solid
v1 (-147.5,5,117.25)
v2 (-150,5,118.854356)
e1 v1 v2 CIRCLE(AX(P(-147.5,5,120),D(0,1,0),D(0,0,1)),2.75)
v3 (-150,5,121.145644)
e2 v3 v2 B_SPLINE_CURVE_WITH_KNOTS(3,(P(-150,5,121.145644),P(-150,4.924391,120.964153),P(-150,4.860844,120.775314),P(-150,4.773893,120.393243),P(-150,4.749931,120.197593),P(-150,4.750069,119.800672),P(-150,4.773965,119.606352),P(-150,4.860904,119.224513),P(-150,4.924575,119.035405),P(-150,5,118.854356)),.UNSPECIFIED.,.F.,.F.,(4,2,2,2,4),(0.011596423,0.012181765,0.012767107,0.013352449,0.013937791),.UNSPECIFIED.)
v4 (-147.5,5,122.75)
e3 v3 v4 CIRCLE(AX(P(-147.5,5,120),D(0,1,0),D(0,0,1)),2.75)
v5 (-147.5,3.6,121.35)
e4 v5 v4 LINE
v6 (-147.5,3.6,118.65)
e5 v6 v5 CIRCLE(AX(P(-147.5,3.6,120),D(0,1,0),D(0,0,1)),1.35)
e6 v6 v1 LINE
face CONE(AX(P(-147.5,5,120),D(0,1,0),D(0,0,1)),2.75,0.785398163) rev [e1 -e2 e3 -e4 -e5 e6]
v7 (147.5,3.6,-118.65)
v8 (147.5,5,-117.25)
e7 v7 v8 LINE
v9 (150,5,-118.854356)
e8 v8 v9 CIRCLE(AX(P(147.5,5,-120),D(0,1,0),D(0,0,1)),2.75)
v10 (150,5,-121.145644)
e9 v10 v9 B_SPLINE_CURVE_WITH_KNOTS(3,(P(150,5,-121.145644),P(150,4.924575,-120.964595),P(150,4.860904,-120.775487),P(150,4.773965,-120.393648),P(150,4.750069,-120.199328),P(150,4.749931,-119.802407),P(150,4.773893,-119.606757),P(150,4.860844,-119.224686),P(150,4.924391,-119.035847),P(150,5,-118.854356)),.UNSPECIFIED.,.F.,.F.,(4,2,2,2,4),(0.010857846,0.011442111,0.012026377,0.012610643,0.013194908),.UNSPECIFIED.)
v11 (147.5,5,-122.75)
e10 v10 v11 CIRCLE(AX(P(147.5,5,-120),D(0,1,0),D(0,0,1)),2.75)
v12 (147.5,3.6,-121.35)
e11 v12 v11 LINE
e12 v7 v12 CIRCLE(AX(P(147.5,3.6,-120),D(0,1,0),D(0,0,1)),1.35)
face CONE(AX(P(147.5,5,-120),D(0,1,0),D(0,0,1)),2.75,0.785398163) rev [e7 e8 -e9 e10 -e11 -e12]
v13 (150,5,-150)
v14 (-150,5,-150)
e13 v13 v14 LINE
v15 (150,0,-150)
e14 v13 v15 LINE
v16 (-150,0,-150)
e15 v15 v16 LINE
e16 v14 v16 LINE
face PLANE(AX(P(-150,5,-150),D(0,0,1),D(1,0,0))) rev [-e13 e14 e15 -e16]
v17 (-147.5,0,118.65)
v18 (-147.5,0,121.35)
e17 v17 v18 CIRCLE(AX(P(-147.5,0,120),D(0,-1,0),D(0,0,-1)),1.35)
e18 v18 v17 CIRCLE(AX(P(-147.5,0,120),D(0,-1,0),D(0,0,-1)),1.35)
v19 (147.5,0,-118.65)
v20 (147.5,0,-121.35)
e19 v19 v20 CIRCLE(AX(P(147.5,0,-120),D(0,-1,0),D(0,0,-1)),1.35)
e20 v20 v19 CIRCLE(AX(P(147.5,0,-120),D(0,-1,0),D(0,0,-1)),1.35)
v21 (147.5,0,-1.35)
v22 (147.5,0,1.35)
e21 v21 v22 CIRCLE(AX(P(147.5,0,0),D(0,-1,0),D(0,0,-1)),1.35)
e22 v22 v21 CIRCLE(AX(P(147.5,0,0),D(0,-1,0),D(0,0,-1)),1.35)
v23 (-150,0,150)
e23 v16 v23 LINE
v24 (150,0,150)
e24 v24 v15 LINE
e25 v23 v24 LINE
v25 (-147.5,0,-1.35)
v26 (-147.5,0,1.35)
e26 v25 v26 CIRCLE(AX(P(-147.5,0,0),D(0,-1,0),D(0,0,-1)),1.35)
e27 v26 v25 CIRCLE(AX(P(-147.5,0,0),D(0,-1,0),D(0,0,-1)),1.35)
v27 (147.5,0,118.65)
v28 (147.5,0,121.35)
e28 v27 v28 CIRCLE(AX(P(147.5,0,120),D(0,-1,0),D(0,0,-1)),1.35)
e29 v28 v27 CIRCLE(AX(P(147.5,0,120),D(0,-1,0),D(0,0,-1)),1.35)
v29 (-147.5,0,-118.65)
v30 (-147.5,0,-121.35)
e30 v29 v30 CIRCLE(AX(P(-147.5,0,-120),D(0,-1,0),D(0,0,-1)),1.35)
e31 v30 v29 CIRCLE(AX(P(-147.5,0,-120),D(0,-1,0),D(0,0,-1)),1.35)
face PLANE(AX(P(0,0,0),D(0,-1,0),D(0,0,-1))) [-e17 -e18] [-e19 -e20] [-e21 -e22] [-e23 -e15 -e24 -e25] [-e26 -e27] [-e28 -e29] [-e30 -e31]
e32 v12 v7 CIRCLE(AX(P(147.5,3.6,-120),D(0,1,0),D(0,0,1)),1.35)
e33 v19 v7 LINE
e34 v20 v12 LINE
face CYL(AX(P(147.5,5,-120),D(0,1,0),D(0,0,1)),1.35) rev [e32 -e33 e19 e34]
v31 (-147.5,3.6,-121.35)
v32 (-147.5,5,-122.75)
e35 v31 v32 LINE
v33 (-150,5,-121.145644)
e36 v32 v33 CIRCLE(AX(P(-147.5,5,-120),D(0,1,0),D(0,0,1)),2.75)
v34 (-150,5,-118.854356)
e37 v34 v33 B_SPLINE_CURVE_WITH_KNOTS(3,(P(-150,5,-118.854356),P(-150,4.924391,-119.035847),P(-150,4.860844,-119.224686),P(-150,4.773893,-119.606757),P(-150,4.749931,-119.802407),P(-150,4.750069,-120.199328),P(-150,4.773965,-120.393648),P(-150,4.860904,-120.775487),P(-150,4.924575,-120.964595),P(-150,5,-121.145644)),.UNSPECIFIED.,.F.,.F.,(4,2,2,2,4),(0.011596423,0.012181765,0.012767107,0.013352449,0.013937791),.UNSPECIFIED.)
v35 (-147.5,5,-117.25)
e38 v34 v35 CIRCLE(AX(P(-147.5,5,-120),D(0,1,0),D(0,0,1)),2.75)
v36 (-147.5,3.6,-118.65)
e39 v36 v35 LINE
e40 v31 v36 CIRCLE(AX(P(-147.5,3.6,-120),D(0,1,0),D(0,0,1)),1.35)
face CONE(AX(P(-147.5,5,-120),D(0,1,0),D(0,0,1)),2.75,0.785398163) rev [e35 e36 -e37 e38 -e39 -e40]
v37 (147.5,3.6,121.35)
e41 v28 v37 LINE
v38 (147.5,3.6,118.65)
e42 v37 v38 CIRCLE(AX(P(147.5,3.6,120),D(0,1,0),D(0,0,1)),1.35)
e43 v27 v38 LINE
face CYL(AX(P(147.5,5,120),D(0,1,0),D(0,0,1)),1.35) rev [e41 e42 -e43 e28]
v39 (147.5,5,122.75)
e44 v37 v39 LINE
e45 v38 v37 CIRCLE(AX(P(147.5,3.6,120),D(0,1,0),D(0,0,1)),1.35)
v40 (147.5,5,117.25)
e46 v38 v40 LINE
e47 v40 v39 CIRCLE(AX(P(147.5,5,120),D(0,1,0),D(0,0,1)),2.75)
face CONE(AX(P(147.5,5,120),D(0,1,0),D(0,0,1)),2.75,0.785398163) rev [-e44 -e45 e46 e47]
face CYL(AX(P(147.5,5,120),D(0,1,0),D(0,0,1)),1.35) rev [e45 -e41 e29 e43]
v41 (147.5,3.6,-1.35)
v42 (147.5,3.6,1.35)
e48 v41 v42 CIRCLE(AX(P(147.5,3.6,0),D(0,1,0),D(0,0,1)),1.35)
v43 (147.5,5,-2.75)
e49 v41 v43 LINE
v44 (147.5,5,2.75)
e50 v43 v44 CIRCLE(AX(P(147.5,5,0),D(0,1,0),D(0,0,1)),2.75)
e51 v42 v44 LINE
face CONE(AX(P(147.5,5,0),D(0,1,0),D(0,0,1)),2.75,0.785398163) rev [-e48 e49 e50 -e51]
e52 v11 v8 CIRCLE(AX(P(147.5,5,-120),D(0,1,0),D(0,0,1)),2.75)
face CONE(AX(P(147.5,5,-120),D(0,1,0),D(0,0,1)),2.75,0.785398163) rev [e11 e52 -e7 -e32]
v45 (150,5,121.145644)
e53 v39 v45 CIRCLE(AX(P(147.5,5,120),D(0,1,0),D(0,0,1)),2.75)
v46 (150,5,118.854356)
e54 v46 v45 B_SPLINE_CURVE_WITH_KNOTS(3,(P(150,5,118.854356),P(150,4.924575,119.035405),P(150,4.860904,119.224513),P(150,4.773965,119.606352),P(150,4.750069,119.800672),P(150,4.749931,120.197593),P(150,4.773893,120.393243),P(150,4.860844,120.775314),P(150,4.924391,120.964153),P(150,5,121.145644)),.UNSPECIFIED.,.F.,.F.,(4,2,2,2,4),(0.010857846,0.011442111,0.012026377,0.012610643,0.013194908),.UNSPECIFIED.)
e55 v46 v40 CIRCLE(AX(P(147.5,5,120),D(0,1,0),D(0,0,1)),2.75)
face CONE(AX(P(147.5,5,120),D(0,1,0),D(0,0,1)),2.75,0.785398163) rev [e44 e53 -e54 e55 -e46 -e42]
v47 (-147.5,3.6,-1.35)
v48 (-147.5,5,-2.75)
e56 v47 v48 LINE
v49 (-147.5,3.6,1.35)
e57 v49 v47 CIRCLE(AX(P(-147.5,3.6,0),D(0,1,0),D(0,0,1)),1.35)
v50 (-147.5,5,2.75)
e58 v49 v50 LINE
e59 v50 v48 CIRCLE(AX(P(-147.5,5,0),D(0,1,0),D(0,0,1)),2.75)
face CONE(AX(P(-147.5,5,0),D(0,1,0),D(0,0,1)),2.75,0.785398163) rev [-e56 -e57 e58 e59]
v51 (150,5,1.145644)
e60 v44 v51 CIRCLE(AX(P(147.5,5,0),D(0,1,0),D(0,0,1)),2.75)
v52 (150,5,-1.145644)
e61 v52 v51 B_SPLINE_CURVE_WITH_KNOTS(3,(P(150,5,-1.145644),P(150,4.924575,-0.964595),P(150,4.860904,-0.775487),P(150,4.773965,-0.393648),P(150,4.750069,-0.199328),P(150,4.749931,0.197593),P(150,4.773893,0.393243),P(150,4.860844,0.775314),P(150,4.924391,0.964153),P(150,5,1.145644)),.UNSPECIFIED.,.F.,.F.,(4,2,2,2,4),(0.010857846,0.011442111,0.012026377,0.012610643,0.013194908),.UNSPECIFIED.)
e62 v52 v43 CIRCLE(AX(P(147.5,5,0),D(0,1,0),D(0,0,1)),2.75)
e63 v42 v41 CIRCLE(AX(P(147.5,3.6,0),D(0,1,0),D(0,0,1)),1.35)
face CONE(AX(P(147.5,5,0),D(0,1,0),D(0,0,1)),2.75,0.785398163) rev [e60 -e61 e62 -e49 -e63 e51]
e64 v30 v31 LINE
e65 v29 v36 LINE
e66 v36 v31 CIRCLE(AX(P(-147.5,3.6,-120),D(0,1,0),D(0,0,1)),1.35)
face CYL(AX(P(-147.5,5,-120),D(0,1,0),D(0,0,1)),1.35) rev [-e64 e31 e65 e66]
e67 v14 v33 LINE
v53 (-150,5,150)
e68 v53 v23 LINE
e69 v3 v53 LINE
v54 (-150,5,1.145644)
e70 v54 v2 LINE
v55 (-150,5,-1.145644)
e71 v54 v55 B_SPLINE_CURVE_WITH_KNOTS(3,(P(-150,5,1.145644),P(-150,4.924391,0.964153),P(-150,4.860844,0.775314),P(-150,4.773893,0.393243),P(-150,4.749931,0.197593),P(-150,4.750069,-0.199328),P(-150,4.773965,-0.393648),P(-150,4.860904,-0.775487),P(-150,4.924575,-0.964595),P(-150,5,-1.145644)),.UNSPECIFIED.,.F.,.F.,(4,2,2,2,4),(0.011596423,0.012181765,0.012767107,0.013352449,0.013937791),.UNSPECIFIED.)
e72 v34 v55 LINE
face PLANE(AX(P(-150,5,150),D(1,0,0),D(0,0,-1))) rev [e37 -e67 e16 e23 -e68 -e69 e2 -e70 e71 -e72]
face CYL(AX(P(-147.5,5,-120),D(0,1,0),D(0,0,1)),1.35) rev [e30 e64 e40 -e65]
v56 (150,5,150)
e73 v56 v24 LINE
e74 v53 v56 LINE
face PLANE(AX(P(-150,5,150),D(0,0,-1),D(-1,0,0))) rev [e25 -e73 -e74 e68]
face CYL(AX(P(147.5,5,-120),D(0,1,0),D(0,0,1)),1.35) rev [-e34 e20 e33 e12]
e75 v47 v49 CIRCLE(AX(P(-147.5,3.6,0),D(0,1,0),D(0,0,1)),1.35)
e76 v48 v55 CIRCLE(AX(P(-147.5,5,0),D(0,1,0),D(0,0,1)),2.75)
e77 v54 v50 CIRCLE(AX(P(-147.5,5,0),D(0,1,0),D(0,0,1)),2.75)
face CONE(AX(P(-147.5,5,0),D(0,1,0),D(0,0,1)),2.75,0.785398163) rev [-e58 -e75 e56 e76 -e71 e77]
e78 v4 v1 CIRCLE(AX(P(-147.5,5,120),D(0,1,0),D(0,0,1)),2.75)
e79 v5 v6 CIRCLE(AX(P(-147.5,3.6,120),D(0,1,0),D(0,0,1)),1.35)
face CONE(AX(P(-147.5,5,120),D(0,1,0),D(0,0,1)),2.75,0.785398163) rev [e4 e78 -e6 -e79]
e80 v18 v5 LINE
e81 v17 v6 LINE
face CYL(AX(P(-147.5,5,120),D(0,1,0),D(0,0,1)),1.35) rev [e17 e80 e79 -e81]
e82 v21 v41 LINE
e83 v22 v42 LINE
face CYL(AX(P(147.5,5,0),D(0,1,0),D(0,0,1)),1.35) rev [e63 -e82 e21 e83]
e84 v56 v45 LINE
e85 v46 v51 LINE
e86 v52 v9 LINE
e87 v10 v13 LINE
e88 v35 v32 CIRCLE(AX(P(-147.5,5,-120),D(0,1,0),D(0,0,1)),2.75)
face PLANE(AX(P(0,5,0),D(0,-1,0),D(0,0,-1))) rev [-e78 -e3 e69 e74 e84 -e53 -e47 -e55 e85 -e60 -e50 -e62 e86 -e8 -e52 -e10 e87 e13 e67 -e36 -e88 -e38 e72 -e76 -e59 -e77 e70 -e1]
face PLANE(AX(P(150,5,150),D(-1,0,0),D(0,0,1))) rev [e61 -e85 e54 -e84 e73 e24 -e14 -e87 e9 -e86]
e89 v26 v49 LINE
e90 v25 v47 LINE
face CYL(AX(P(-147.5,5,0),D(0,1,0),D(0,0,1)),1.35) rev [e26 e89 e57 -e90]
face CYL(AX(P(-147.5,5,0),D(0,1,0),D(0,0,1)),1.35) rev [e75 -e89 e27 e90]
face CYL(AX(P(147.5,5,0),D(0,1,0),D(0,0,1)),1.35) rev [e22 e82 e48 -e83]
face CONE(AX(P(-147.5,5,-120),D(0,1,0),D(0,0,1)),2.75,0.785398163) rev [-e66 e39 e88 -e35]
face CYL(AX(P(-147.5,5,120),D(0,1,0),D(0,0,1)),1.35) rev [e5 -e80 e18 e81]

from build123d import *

# Parameters (mm, degrees)
SKETCH1_W                                         = 300
SKETCH1_H                                         = 300
BOSS_EXTRUDE1_DEPTH                               = 5
CSK_FOR_M2_5_FLAT_HEAD_MACHINE_SCREW1_D           = 2.7
CSK_FOR_M2_5_FLAT_HEAD_MACHINE_SCREW1_DEPTH       = 17
CSK_FOR_M2_5_FLAT_HEAD_MACHINE_SCREW1_CSINK_D     = 5.5
CSK_FOR_M2_5_FLAT_HEAD_MACHINE_SCREW1_CSINK_ANGLE = 90
CSK_FOR_M2_5_FLAT_HEAD_MACHINE_SCREW1_TIP         = 0.811161836


with BuildPart() as part:
    # Sketch1 → Boss-Extrude1 (new body)
    with BuildSketch(Plane(origin=(0, 0, 0), x_dir=(1, 0, 0), z_dir=(0, 1, 0))):
        Rectangle(SKETCH1_W, SKETCH1_H)
    extrude(amount=BOSS_EXTRUDE1_DEPTH)

    # CSK for M2.5 Flat Head Machine Screw1
    with Locations(Plane(origin=(0, 5, 0), x_dir=(1, 0, 0), z_dir=(0, 1, 0))):
        with Locations((147.5, 120), (147.5, 0), (147.5, -120), (-147.5, 120), (-147.5, 0), (-147.5, -120)):
            CounterSinkHole(CSK_FOR_M2_5_FLAT_HEAD_MACHINE_SCREW1_D / 2, CSK_FOR_M2_5_FLAT_HEAD_MACHINE_SCREW1_CSINK_D / 2, depth=CSK_FOR_M2_5_FLAT_HEAD_MACHINE_SCREW1_DEPTH, counter_sink_angle=CSK_FOR_M2_5_FLAT_HEAD_MACHINE_SCREW1_CSINK_ANGLE)
            with Locations((0, 0, -(CSK_FOR_M2_5_FLAT_HEAD_MACHINE_SCREW1_DEPTH + CSK_FOR_M2_5_FLAT_HEAD_MACHINE_SCREW1_TIP / 2))):  # 118° drill point
                Cone(0, CSK_FOR_M2_5_FLAT_HEAD_MACHINE_SCREW1_D / 2, CSK_FOR_M2_5_FLAT_HEAD_MACHINE_SCREW1_TIP, mode=Mode.SUBTRACT)


solid = part.part
